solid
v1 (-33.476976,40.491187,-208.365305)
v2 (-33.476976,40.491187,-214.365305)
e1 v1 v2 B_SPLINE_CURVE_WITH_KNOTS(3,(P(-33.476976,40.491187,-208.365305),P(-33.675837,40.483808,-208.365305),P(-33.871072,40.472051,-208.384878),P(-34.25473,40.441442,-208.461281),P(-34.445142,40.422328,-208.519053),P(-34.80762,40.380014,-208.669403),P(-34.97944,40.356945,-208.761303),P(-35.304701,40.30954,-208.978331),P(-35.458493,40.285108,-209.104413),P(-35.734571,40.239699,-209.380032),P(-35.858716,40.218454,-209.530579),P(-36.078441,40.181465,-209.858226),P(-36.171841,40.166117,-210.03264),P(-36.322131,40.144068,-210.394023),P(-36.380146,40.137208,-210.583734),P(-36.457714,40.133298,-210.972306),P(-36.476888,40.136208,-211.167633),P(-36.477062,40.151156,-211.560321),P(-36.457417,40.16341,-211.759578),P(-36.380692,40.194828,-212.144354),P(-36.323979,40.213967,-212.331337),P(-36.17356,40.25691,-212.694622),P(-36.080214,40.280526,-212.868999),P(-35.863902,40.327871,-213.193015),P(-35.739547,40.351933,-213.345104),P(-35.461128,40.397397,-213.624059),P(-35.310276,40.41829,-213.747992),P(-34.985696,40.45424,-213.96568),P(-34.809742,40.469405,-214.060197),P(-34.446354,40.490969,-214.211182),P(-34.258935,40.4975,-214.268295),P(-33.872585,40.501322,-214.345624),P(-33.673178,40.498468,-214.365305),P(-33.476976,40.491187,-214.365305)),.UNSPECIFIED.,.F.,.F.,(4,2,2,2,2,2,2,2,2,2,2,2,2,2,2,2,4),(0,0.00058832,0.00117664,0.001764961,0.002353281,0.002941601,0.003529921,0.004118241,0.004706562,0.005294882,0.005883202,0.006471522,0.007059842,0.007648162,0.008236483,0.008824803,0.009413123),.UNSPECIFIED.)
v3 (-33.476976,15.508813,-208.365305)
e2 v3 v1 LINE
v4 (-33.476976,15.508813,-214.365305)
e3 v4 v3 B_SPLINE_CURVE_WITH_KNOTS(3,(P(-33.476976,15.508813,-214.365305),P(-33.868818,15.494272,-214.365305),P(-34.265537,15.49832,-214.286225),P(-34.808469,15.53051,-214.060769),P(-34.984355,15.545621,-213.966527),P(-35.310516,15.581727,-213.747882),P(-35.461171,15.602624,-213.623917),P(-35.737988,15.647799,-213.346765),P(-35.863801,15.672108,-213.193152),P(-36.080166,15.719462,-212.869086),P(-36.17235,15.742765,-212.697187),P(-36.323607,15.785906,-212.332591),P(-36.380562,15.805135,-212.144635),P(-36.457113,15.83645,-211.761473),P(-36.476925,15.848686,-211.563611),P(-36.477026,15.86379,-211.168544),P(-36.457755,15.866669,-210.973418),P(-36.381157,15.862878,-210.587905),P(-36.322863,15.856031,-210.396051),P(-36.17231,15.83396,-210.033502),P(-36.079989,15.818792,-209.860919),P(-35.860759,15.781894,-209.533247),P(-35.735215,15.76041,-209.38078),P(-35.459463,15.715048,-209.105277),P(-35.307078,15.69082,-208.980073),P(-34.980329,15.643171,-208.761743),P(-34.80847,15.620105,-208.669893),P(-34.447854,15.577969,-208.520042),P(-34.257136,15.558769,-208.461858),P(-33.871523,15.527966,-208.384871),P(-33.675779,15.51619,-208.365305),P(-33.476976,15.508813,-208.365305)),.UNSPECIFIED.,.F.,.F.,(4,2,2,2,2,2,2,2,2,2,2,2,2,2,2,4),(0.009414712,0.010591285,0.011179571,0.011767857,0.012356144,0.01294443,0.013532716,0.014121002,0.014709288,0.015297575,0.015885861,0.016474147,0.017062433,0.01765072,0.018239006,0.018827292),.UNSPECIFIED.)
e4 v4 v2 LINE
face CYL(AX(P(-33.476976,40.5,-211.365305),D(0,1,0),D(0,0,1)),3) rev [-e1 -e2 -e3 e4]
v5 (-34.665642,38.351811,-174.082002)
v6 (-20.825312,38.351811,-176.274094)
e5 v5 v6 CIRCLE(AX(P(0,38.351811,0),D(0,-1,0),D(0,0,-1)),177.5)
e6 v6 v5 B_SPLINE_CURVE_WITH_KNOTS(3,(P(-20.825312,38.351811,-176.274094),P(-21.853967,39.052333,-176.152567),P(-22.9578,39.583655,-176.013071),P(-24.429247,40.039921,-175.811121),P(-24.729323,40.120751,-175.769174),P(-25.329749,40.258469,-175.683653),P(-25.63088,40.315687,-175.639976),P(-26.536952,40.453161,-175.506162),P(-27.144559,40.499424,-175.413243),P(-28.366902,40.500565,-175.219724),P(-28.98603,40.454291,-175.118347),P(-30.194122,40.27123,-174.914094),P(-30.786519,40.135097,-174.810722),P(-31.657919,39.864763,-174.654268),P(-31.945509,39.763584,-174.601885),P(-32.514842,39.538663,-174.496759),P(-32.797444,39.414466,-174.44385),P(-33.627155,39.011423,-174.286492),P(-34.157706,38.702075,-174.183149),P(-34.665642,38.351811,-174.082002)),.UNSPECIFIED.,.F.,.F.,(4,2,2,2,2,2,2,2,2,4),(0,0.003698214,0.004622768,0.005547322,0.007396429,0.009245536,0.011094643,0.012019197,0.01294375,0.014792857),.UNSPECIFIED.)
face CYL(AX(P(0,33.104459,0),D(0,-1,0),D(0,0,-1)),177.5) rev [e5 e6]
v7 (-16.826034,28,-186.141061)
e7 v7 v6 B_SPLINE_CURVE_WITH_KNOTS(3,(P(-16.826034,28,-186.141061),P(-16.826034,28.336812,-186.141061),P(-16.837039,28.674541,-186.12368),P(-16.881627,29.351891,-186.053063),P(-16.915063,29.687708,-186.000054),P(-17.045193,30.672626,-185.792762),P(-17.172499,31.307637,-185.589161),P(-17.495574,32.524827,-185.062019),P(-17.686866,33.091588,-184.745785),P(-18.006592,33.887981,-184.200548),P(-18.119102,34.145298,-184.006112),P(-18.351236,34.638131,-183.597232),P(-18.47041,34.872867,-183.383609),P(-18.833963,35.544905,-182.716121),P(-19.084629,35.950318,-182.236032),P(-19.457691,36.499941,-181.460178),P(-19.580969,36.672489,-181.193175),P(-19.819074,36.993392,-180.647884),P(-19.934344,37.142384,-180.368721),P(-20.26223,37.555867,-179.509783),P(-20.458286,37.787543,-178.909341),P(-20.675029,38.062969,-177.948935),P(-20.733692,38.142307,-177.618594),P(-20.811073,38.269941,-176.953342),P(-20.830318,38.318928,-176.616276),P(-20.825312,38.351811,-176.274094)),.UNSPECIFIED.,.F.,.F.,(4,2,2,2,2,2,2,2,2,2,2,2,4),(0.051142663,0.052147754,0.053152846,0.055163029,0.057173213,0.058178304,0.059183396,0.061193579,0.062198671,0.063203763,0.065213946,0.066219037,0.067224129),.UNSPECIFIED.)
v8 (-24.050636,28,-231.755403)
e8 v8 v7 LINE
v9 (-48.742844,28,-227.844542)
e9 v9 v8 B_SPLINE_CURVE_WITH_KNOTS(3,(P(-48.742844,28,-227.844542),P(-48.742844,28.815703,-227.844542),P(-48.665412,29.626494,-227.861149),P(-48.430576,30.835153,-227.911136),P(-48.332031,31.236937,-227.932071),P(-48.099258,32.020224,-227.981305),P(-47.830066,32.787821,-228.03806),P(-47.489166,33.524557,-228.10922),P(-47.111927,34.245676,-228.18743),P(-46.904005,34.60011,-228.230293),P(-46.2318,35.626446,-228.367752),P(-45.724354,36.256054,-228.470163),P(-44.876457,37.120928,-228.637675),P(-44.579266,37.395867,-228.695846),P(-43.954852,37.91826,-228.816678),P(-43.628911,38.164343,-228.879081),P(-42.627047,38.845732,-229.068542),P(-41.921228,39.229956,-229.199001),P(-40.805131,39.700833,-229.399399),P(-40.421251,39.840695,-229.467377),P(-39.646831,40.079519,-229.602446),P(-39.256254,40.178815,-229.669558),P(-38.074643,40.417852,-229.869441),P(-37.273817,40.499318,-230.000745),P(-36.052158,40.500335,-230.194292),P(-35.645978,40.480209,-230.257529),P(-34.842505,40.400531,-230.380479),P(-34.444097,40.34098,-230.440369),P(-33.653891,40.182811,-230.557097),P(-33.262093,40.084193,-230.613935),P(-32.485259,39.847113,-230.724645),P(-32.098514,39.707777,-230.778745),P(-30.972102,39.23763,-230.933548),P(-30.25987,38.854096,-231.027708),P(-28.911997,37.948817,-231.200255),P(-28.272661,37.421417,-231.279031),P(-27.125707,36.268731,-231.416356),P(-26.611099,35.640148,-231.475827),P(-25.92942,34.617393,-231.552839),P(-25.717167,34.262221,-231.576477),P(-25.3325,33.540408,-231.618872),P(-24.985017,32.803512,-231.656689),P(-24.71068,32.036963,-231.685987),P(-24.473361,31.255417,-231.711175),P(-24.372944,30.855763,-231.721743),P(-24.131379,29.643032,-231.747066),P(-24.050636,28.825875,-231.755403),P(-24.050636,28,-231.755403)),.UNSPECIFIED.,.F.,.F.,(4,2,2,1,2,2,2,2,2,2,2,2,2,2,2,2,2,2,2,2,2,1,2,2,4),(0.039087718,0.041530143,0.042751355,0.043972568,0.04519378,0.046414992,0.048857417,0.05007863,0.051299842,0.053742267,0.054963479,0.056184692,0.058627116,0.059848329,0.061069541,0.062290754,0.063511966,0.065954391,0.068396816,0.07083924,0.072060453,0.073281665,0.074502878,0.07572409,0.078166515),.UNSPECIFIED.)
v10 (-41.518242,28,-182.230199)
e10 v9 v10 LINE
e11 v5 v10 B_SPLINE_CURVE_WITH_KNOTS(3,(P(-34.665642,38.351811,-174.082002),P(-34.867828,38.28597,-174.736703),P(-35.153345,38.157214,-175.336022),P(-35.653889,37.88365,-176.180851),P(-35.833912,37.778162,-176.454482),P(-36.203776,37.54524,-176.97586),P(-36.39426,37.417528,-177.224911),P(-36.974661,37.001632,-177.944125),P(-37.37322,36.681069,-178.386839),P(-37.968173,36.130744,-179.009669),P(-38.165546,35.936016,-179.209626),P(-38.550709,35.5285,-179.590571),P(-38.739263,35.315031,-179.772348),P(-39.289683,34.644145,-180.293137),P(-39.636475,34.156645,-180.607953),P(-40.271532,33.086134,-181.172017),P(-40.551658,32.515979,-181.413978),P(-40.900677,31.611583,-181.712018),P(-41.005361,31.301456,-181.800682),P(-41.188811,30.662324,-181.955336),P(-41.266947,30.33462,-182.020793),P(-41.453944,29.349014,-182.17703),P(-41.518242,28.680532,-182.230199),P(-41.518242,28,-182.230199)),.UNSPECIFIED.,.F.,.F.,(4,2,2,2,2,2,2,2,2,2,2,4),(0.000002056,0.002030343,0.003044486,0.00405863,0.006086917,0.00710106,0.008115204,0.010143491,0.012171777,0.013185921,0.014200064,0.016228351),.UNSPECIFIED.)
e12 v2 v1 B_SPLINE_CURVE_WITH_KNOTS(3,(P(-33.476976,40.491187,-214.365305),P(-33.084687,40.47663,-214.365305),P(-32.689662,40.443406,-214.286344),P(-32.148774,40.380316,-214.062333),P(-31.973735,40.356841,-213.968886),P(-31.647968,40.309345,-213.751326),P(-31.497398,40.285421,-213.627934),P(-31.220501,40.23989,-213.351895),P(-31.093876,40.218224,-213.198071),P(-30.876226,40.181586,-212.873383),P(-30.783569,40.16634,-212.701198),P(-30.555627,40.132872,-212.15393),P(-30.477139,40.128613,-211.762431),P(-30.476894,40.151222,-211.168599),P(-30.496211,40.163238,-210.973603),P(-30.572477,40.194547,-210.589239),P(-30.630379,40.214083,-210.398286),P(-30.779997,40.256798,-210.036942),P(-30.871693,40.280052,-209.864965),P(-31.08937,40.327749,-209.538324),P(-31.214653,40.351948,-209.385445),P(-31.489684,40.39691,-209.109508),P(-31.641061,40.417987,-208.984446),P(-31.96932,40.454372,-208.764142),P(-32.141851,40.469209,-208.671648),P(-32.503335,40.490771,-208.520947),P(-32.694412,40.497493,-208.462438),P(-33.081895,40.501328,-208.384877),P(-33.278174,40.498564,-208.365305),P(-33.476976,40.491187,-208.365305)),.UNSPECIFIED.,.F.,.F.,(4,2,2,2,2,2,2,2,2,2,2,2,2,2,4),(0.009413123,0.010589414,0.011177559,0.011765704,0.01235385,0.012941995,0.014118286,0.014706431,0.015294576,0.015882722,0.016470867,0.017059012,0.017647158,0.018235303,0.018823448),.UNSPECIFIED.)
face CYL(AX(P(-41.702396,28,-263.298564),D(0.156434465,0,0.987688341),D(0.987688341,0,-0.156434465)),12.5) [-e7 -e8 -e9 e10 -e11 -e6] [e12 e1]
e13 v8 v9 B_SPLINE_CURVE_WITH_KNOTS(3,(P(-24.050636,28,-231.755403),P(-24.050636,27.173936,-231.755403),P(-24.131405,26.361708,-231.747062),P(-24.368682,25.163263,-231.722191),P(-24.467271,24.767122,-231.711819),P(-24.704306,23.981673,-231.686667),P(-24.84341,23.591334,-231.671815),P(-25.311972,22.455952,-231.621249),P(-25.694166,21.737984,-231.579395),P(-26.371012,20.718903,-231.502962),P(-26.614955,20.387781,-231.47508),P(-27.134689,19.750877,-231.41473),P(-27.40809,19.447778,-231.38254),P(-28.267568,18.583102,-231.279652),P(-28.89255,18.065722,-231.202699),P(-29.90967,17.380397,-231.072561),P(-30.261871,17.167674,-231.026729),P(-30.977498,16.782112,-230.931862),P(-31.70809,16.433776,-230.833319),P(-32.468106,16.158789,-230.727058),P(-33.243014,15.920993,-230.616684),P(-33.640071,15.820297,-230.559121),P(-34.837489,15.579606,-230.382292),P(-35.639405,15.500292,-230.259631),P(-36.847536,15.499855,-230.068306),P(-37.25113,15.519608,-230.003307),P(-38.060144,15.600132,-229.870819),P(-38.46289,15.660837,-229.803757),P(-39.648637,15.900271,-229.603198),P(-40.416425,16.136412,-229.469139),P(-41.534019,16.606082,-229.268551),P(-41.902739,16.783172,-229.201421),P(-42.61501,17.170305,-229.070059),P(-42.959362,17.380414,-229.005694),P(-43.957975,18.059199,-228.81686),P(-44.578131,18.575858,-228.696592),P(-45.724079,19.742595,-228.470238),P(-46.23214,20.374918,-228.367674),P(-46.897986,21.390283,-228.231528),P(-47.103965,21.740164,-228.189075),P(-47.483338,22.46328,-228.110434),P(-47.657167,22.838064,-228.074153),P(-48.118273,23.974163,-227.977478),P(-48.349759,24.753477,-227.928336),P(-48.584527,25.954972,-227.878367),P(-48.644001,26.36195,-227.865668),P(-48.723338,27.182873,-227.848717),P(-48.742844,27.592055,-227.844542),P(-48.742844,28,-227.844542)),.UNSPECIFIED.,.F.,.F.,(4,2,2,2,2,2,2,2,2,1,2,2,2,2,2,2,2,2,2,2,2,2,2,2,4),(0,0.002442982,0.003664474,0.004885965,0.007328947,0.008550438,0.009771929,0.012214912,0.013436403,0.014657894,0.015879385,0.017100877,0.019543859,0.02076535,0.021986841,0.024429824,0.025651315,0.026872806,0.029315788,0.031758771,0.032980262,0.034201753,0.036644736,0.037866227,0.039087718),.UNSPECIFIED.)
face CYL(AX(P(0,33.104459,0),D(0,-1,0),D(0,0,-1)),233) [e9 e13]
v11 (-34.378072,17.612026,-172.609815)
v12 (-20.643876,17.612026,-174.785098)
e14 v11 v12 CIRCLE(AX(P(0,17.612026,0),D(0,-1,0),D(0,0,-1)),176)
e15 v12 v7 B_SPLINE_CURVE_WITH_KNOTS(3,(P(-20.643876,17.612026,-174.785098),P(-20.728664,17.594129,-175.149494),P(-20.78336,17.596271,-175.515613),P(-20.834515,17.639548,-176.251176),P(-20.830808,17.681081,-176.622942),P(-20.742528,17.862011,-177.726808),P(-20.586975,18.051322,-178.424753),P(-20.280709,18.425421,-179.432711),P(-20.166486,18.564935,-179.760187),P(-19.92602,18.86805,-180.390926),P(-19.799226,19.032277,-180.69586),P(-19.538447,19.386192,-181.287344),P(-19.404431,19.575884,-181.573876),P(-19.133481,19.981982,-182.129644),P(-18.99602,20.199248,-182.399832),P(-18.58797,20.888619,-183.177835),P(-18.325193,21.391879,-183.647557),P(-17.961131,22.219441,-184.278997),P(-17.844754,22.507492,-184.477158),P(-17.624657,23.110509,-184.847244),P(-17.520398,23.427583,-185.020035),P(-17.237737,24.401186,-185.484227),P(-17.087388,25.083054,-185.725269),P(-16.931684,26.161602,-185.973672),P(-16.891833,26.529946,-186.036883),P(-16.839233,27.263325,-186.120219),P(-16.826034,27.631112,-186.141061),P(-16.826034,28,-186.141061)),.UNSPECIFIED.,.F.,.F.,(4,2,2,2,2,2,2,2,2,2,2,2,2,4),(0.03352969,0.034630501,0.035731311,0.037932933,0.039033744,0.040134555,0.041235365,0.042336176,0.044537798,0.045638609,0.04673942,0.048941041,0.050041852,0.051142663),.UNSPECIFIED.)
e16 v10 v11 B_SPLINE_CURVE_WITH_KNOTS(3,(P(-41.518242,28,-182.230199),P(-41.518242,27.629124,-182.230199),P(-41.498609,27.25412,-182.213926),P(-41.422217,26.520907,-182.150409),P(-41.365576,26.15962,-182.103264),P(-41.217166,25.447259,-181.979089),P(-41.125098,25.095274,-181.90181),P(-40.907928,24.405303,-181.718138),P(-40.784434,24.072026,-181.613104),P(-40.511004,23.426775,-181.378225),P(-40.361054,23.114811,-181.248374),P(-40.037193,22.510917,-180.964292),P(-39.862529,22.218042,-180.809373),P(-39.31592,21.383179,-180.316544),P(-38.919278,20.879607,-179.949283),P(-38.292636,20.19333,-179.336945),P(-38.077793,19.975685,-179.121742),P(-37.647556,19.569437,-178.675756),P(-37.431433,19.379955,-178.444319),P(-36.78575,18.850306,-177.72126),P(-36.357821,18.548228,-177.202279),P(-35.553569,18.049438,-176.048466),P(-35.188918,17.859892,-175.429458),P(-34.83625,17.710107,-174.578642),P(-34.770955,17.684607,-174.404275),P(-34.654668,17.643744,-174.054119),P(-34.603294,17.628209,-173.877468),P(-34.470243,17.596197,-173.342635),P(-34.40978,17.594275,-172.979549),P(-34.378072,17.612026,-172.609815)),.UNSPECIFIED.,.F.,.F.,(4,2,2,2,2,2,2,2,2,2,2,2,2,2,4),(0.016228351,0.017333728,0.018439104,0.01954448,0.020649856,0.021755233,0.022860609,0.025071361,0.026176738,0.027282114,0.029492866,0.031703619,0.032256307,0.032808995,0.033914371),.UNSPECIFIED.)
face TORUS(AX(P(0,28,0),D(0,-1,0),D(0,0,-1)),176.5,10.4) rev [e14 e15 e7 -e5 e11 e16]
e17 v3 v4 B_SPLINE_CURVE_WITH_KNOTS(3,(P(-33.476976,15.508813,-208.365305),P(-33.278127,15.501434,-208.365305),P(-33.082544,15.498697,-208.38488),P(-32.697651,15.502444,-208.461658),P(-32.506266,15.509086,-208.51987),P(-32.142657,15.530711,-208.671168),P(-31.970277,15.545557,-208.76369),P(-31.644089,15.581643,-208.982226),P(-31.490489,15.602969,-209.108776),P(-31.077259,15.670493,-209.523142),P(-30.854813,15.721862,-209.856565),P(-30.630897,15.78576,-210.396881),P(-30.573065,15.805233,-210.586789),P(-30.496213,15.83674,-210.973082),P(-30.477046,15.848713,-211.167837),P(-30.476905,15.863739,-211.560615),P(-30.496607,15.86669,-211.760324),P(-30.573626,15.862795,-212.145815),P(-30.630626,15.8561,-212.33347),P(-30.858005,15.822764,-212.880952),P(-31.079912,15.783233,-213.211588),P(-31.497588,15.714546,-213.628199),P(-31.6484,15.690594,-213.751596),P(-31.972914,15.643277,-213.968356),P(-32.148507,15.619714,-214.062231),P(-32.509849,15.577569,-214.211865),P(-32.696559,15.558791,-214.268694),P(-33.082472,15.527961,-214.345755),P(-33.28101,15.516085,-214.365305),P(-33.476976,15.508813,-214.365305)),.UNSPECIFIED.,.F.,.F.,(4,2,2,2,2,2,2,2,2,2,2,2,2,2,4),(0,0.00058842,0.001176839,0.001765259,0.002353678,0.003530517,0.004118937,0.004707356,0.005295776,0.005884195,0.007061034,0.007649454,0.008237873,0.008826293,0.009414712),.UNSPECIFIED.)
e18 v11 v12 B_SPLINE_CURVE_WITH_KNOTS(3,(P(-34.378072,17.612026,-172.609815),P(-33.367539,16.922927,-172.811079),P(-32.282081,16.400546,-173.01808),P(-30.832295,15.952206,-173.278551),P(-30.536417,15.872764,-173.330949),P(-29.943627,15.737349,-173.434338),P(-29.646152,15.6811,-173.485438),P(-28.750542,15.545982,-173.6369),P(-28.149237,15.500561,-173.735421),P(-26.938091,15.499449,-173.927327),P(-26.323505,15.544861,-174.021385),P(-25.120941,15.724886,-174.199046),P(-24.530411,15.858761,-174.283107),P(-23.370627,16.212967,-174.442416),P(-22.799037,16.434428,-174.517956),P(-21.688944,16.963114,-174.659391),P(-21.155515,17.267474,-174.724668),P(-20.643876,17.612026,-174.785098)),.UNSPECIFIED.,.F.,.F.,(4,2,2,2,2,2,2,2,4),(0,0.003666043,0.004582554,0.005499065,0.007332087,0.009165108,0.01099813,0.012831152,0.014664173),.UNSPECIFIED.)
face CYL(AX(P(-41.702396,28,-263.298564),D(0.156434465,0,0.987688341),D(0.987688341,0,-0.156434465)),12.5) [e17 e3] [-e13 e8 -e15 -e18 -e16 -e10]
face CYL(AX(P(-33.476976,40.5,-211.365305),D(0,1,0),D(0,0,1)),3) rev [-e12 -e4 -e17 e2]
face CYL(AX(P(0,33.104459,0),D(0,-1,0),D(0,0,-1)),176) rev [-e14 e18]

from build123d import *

# Parameters (mm, degrees)
HOLE_SIZE_PER_SOCKET_HEAD_CAP_SCREW_TYPE_D           = 18
HOLE_SIZE_PER_SOCKET_HEAD_CAP_SCREW_TYPE_CBORE_D     = 26
HOLE_SIZE_PER_SOCKET_HEAD_CAP_SCREW_TYPE_CBORE_DEPTH = 21
CIRPATTERN2_COUNT                                    = 20
SKETCH5_OUTSIDE_W                                    = 667.458
SKETCH5_OUTSIDE_H                                    = 191.296
SKETCH5_OUTSIDE_R                                    = 12.5
CUT_EXTRUDE2_DEPTH                                   = 335.405442539
F_6_0_6_DIAMETER_HOLE1_D                             = 6


with BuildPart() as part:
    # Sketch1 → Revolve1 (revolve)
    with BuildSketch(Plane.XY, mode=Mode.PRIVATE) as revolve1_sk:
        with BuildLine():
            Line((-176, 0), (-233, 0))
            Line((-233, 0), (-233, 46))
            Line((-233, 46), (-196, 46))
            Line((-196, 46), (-196, 47))
            Line((-196, 47), (-194.03, 47))
            Line((-194.03, 47), (-194.03, 51))
            Line((-194.03, 51), (-196, 51))
            Line((-196, 51), (-196, 57))
            Line((-196, 57), (-190.3, 57))
            Line((-190.3, 57), (-190.3, 53.2))
            Line((-190.3, 53.2), (-183, 53.2))
            Line((-183, 53.2), (-183, 57))
            Line((-183, 57), (-179.375644347, 57))
            Line((-179.375644347, 57), (-177.5, 50))
            Line((-177.5, 50), (-177.5, 38.351811436))
            ThreePointArc((-177.5, 38.351811436), (-186.87290572, 27.249782079), (-176, 17.612026184))
            Line((-176, 17.612026184), (-176, 8.5))
            Line((-176, 8.5), (-184, 8.5))
            Line((-184, 8.5), (-184, 4.5))
            Line((-184, 4.5), (-176, 4.5))
            Line((-176, 4.5), (-176, 0))
        make_face()
    revolve(revolve1_sk.sketch.rotate(Axis((0, 33.104458612, 0), (0, 1, 0)), 270), axis=Axis((0, 33.104458612, 0), (0, 1, 0)))

    # Hole size per socket head cap screw type1 (through all)
    with Locations(Plane.XZ):
        with Locations((-214, 0)):
            hole_size_per_socket_head_cap_screw_type = CounterBoreHole(HOLE_SIZE_PER_SOCKET_HEAD_CAP_SCREW_TYPE_D / 2, HOLE_SIZE_PER_SOCKET_HEAD_CAP_SCREW_TYPE_CBORE_D / 2, HOLE_SIZE_PER_SOCKET_HEAD_CAP_SCREW_TYPE_CBORE_DEPTH)

    # CirPattern2: Hole size per socket head cap screw type1 ×20 about axis
    cirpattern2_axis = Axis((0, 0, 0), (0, 1, 0))
    for i in range(1, CIRPATTERN2_COUNT):
        add(hole_size_per_socket_head_cap_screw_type.rotate(cirpattern2_axis, i * 360 / CIRPATTERN2_COUNT), mode=Mode.SUBTRACT)

    # Sketch5 outside → Cut-Extrude2 (cut, through all)
    with BuildSketch(Plane(origin=(0, 0, 0), x_dir=(-0.9876883405951378, 0, 0.15643446504023129), z_dir=(-0.15643446504023129, 0, -0.9876883405951378))):
        with Locations((0, 28.5)):
            Rectangle(SKETCH5_OUTSIDE_W, SKETCH5_OUTSIDE_H)
        with Locations(Location((0, 28, 0), (0, 0, 180))):
            Circle(SKETCH5_OUTSIDE_R, mode=Mode.SUBTRACT)
    extrude(amount=CUT_EXTRUDE2_DEPTH, mode=Mode.SUBTRACT)


with BuildPart() as body_2:
    # of the pieces the cut leaves, the one that is kept (cut_extrude2_keep)
    add(part.part.solids().sort_by_distance((-20.643876308, 17.612026184, -174.78509768))[0])

    # Ø6.0 (6) Diameter Hole1 (through all)
    with Locations(Plane(origin=(-33.476975519, 40.5, -211.365304887), x_dir=(0, 0, 1), z_dir=(0, 1, 0))):
        with Locations((0, 0)):
            Hole(F_6_0_6_DIAMETER_HOLE1_D / 2)


solid = body_2.part
